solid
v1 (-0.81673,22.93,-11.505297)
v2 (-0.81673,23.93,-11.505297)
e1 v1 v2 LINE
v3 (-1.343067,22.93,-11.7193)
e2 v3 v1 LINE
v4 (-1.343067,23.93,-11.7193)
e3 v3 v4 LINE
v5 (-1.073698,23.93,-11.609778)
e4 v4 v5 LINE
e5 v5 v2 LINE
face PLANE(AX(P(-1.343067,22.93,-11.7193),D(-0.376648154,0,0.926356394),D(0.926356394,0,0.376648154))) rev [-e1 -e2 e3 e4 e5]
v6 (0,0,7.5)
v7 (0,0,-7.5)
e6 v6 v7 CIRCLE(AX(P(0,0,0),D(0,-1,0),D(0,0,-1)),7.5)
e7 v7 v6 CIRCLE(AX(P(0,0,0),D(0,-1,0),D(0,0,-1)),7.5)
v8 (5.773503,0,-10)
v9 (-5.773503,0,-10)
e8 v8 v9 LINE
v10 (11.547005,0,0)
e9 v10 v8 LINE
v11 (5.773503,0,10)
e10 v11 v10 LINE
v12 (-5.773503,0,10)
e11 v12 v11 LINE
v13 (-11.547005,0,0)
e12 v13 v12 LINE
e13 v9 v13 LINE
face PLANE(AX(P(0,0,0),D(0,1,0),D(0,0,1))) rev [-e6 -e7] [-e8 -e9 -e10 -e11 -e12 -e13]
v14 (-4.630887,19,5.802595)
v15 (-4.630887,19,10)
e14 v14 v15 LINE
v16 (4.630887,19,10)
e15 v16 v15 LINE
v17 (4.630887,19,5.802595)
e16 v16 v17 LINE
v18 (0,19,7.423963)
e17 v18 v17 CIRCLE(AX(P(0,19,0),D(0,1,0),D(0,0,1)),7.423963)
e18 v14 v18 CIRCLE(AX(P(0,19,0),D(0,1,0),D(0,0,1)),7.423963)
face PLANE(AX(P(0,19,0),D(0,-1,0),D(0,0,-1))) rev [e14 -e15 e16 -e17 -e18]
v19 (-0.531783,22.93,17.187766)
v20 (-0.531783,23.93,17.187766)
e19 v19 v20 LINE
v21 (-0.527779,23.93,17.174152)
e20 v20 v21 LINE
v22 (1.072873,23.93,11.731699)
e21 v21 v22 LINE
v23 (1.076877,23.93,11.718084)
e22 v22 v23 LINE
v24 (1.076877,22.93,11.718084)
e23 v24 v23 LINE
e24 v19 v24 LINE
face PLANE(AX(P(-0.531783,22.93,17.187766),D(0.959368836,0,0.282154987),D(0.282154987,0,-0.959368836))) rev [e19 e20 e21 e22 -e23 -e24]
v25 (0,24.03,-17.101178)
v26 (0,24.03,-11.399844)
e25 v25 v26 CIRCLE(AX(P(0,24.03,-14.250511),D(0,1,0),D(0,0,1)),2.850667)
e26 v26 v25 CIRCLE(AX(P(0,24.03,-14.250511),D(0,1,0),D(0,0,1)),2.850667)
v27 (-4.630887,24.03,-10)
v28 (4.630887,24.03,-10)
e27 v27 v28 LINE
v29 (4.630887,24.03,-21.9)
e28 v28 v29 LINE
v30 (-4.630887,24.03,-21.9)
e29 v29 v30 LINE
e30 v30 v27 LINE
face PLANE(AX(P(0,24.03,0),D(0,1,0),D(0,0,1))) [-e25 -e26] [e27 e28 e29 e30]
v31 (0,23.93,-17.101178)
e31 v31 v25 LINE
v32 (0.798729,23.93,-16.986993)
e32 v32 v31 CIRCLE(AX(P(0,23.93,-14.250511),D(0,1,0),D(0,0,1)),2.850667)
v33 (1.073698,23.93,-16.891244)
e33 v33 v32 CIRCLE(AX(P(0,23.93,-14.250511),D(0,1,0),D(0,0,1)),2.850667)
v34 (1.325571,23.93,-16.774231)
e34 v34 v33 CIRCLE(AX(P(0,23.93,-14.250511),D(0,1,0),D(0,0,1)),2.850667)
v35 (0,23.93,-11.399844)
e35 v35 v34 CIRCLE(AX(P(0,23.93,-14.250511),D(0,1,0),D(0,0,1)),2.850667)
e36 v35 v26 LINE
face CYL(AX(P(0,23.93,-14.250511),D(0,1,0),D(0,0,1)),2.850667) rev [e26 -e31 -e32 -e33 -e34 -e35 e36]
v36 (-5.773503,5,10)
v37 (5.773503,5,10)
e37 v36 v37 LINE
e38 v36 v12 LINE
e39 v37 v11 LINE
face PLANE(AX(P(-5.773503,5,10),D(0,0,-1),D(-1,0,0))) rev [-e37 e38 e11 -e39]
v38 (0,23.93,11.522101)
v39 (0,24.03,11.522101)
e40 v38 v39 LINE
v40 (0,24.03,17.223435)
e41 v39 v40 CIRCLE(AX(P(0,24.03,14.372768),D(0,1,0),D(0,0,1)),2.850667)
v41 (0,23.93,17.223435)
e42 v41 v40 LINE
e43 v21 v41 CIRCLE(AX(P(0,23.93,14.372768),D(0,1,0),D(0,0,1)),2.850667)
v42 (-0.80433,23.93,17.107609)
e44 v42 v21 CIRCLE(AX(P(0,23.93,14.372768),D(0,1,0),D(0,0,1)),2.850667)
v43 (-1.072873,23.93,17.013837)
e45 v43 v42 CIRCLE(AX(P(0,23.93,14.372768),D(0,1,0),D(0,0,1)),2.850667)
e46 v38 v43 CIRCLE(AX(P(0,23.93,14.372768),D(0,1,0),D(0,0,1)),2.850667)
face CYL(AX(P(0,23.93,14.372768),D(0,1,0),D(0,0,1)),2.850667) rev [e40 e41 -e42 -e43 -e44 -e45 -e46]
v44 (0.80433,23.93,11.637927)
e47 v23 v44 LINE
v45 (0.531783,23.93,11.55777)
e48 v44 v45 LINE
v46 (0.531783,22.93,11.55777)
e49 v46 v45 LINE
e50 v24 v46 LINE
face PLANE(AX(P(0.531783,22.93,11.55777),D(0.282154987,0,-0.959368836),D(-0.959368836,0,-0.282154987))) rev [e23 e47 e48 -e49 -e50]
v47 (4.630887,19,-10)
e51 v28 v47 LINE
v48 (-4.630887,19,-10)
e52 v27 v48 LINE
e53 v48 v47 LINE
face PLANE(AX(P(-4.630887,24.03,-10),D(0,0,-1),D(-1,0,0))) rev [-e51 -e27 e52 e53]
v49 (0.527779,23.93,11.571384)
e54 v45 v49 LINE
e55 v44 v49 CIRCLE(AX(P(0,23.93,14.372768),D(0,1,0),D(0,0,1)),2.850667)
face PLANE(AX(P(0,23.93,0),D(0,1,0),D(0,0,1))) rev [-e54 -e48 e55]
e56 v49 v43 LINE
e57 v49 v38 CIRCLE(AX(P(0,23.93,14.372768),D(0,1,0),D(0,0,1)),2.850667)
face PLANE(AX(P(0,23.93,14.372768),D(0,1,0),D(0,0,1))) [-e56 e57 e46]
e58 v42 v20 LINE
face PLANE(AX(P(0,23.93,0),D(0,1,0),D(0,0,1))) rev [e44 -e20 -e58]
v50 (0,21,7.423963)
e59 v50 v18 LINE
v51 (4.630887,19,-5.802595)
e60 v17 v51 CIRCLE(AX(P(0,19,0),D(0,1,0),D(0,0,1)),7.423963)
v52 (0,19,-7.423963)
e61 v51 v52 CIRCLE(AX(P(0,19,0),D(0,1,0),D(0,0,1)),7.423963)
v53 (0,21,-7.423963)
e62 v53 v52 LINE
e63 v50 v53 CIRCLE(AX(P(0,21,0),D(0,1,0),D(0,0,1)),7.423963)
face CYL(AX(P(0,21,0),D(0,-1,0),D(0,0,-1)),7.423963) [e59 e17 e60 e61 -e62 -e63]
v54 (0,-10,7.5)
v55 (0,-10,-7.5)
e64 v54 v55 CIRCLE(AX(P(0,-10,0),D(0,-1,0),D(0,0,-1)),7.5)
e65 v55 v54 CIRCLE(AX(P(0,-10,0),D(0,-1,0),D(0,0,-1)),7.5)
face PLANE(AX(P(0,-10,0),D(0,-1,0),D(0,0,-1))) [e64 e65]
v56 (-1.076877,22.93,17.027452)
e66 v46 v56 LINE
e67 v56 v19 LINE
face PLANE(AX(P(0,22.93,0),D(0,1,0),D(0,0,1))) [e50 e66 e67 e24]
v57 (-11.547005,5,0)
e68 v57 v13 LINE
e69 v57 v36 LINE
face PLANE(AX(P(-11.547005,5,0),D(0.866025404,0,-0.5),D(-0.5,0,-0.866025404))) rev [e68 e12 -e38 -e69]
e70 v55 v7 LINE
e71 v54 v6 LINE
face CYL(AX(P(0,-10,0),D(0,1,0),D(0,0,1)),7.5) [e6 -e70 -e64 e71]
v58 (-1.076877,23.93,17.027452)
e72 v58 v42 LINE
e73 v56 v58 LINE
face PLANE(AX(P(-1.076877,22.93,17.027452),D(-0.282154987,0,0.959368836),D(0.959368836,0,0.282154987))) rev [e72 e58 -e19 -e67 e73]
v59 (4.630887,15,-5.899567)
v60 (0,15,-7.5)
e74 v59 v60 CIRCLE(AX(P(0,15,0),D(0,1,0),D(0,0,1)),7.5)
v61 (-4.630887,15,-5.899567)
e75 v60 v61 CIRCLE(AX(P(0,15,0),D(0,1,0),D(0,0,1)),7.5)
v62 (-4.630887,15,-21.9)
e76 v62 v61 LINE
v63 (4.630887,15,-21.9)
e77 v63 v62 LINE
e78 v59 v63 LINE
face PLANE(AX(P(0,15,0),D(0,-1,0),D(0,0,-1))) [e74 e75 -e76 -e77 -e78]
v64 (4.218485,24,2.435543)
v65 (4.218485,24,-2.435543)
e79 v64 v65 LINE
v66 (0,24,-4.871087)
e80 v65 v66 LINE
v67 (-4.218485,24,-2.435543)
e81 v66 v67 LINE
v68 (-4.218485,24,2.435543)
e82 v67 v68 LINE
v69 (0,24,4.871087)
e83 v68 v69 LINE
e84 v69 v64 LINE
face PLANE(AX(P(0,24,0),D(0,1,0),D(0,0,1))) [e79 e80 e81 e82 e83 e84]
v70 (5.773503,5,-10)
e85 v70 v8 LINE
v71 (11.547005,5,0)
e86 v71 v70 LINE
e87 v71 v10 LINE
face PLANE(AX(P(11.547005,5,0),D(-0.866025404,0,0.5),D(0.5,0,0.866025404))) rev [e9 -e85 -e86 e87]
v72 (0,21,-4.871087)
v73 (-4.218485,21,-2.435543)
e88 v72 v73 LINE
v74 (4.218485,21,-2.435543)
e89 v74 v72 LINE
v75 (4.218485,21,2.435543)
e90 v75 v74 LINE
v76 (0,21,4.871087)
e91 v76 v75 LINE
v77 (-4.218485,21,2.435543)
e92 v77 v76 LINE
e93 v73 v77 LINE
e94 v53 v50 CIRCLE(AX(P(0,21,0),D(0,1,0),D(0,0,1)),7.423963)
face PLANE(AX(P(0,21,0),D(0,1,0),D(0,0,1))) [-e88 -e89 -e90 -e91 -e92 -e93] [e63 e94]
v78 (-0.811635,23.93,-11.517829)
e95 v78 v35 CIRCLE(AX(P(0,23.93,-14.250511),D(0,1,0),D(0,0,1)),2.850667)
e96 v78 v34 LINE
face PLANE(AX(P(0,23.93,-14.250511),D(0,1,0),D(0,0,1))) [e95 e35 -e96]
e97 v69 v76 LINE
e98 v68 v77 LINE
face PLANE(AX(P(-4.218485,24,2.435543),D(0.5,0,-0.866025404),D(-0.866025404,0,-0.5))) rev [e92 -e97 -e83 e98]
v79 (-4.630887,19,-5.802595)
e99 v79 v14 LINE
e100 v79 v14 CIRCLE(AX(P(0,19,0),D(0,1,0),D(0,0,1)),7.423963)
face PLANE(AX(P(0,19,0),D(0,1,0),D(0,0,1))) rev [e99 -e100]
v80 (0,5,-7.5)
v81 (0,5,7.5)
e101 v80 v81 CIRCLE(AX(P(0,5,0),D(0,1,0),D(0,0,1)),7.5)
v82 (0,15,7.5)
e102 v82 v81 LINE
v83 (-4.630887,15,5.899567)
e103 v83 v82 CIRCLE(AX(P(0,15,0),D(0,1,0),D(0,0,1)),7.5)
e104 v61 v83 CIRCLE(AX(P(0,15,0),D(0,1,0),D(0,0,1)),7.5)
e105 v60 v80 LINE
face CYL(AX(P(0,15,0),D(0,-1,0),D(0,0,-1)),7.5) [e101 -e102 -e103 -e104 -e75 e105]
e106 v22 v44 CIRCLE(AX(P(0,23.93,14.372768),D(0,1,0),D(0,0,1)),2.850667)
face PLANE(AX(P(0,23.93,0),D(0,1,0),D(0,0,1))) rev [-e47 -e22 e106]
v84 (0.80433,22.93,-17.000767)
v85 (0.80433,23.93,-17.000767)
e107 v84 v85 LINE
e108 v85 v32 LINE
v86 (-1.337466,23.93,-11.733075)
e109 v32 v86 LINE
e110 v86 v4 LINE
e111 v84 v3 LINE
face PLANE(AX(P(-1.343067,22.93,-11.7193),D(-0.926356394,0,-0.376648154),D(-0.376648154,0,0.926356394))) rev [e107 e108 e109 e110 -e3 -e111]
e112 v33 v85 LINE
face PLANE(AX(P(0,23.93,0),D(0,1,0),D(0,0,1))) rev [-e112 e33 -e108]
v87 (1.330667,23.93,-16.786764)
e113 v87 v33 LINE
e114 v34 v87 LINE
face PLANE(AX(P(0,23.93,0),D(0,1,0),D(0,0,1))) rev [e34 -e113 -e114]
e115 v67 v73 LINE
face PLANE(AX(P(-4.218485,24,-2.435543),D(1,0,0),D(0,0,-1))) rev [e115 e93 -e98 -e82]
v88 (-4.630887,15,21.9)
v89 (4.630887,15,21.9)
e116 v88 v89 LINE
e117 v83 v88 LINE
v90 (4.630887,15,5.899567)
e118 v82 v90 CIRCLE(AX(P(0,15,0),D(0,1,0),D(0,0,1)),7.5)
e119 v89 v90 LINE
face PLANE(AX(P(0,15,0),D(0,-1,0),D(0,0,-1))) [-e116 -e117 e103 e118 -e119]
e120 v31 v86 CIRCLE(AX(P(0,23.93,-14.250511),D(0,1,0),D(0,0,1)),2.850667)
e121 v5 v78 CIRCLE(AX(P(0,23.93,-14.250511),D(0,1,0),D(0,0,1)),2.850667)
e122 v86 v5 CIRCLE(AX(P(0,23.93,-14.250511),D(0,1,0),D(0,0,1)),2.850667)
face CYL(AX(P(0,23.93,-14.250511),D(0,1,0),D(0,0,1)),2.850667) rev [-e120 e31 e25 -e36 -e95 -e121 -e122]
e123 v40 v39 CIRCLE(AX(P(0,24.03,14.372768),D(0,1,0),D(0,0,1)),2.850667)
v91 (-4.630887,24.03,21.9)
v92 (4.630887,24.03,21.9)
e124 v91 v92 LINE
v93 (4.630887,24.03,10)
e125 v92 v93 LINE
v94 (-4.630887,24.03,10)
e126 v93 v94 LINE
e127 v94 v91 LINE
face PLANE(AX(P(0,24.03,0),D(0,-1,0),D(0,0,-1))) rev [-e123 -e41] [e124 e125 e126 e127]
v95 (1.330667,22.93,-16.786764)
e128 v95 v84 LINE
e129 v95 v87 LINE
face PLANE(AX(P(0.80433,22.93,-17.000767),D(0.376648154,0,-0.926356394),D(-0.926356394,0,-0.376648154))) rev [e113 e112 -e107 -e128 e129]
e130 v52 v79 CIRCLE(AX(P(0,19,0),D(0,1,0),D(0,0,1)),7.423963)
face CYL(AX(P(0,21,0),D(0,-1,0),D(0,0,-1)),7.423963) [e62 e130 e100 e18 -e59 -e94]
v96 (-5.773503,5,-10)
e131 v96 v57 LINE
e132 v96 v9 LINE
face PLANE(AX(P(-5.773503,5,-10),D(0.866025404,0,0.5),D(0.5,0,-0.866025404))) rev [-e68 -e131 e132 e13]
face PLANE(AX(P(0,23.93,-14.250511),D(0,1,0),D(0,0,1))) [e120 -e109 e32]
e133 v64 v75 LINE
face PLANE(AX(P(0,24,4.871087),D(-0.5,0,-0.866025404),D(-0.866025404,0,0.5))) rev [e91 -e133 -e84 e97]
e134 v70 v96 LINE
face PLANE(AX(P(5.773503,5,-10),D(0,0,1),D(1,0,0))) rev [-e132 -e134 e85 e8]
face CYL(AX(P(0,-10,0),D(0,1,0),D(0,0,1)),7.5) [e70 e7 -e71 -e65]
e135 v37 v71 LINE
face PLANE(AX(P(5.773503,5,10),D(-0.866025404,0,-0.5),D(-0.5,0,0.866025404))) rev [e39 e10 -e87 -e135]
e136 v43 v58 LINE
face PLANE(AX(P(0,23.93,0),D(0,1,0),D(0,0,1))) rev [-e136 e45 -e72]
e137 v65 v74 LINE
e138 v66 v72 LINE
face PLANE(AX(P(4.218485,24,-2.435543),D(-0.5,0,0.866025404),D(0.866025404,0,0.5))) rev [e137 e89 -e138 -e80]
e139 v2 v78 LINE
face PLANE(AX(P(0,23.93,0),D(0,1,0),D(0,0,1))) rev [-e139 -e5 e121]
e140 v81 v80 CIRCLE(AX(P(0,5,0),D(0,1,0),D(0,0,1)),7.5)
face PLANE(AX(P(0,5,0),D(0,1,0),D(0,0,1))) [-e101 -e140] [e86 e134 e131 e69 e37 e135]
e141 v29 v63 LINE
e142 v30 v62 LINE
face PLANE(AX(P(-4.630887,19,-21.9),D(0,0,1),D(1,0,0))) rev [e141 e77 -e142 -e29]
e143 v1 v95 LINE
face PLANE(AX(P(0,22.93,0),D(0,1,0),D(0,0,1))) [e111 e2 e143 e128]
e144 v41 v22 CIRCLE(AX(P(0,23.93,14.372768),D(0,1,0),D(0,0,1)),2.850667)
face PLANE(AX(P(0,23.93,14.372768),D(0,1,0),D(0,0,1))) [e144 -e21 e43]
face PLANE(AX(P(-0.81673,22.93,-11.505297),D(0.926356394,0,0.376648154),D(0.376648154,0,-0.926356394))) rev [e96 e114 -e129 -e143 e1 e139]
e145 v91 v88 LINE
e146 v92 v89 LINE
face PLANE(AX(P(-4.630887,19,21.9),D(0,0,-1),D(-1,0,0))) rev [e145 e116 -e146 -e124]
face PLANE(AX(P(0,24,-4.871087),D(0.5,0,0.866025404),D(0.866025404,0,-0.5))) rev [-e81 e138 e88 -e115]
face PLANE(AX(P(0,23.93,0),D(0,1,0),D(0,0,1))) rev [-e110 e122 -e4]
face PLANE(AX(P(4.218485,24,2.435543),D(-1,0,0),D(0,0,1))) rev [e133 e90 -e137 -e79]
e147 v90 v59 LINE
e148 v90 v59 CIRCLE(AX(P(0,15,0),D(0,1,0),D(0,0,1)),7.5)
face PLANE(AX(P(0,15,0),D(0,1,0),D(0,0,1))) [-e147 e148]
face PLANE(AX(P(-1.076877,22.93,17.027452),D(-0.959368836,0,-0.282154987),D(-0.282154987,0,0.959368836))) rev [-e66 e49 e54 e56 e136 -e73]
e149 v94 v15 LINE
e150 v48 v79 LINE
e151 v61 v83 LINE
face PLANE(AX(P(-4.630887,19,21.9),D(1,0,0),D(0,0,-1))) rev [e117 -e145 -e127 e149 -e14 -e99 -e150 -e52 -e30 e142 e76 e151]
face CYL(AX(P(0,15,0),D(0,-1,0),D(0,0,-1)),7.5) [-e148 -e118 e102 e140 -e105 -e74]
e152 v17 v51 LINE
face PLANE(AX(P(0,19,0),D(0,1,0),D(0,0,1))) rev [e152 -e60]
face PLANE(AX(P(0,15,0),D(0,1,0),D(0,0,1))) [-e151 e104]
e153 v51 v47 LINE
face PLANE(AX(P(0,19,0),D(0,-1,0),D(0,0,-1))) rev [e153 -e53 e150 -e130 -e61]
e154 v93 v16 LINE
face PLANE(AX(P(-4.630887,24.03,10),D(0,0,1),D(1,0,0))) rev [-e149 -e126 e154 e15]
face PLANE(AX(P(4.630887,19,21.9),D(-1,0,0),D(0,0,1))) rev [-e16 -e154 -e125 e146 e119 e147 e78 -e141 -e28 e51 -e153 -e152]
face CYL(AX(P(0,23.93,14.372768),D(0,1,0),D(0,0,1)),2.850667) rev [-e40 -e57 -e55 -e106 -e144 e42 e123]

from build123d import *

# Parameters (mm, degrees)
BOSS_EXTRUDE1_DEPTH = 5
SKETCH2_R           = 7.5
BOSS_EXTRUDE2_DEPTH = 10
BOSS_EXTRUDE7_START = 10
SKETCH9_R           = 7.5
BOSS_EXTRUDE7_DEPTH = 10
SKETCH3_W           = 9.261773254
SKETCH3_H           = 43.8
BOSS_EXTRUDE3_DEPTH = 4
SKETCH4_W           = 9.261773254
SKETCH4_H           = 11.9
BOSS_EXTRUDE4_DEPTH = 5.03
SKETCH5_R           = 7.423962758
BOSS_EXTRUDE5_DEPTH = 2
BOSS_EXTRUDE6_DEPTH = 3
SKETCH7_R           = 2.850666807
CUT_EXTRUDE1_DEPTH  = 0.1
CUT_EXTRUDE2_DEPTH  = 1


with BuildPart() as part:
    # Sketch1 → Boss-Extrude1 (new body)
    with BuildSketch(Plane(origin=(0, 0, 0), x_dir=(1, 0, 0), z_dir=(0, 1, 0))):
        Polygon((5.773502692, 10), (-5.773502692, 10), (-11.547005384, 0), (-5.773502692, -10), (5.773502692, -10), (11.547005384, 0), align=None)
    extrude(amount=BOSS_EXTRUDE1_DEPTH)

    # Sketch2 → Boss-Extrude2 (add)
    with BuildSketch(Plane.XZ):
        with Locations(Location((0, 0, 0), (0, 0, 270))):
            Circle(SKETCH2_R)
    extrude(amount=BOSS_EXTRUDE2_DEPTH)

    # Sketch9 → Boss-Extrude7 (add)
    with BuildSketch(Plane(origin=(0, 5, 0), x_dir=(1, 0, 0), z_dir=(0, 1, 0)).offset(BOSS_EXTRUDE7_START)):
        with Locations(Location((0, 0, 0), (0, 0, 90))):
            Circle(SKETCH9_R)
    extrude(amount=-BOSS_EXTRUDE7_DEPTH)

    # Sketch3 → Boss-Extrude3 (add)
    with BuildSketch(Plane(origin=(0, 15, 0), x_dir=(1, 0, 0), z_dir=(0, 1, 0))):
        Rectangle(SKETCH3_W, SKETCH3_H)
    extrude(amount=BOSS_EXTRUDE3_DEPTH)

    # Sketch4 → Boss-Extrude4 (add)
    with BuildSketch(Plane(origin=(0, 19, 0), x_dir=(1, 0, 0), z_dir=(0, 1, 0))):
        with Locations((0, 15.95)):
            Rectangle(SKETCH4_W, SKETCH4_H)
        with Locations((0, -15.95)):
            Rectangle(SKETCH4_W, SKETCH4_H)
    extrude(amount=BOSS_EXTRUDE4_DEPTH)

    # Sketch5 → Boss-Extrude5 (add)
    with BuildSketch(Plane(origin=(0, 19, 0), x_dir=(1, 0, 0), z_dir=(0, 1, 0))):
        with Locations(Location((0, 0, 0), (0, 0, 51.407625877))):
            Circle(SKETCH5_R)
    extrude(amount=BOSS_EXTRUDE5_DEPTH)

    # Sketch6 → Boss-Extrude6 (add)
    with BuildSketch(Plane(origin=(0, 21, 0), x_dir=(1, 0, 0), z_dir=(0, 1, 0))):
        Polygon((0, 4.871086868), (-4.218484972, 2.435543434), (-4.218484972, -2.435543434), (0, -4.871086868), (4.218484972, -2.435543434), (4.218484972, 2.435543434), align=None)
    extrude(amount=BOSS_EXTRUDE6_DEPTH)

    # Sketch7 → Cut-Extrude1 (cut)
    with BuildSketch(Plane(origin=(0, 24.03, 0), x_dir=(1, 0, 0), z_dir=(0, 1, 0))):
        with Locations(Location((0, 14.250511049, 0), (0, 0, 270))):
            Circle(SKETCH7_R)
        with Locations(Location((0, -14.372767949, 0), (0, 0, 270))):
            Circle(SKETCH7_R)
    extrude(amount=-CUT_EXTRUDE1_DEPTH, mode=Mode.SUBTRACT)

    # Sketch8 → Cut-Extrude2 (cut)
    with BuildSketch(Plane(origin=(0, 23.93, 0), x_dir=(1, 0, 0), z_dir=(0, 1, 0))):
        Polygon((-1.343066927, 11.719300444), (0.804329856, 17.000767289), (1.330666503, 16.786763555), (-0.81673028, 11.505296711), align=None)
        Polygon((-1.076876675, -17.027451515), (0.531783037, -11.557769723), (1.076876675, -11.718084383), (-0.531783037, -17.187766175), align=None)
    extrude(amount=-CUT_EXTRUDE2_DEPTH, mode=Mode.SUBTRACT)


solid = part.part
